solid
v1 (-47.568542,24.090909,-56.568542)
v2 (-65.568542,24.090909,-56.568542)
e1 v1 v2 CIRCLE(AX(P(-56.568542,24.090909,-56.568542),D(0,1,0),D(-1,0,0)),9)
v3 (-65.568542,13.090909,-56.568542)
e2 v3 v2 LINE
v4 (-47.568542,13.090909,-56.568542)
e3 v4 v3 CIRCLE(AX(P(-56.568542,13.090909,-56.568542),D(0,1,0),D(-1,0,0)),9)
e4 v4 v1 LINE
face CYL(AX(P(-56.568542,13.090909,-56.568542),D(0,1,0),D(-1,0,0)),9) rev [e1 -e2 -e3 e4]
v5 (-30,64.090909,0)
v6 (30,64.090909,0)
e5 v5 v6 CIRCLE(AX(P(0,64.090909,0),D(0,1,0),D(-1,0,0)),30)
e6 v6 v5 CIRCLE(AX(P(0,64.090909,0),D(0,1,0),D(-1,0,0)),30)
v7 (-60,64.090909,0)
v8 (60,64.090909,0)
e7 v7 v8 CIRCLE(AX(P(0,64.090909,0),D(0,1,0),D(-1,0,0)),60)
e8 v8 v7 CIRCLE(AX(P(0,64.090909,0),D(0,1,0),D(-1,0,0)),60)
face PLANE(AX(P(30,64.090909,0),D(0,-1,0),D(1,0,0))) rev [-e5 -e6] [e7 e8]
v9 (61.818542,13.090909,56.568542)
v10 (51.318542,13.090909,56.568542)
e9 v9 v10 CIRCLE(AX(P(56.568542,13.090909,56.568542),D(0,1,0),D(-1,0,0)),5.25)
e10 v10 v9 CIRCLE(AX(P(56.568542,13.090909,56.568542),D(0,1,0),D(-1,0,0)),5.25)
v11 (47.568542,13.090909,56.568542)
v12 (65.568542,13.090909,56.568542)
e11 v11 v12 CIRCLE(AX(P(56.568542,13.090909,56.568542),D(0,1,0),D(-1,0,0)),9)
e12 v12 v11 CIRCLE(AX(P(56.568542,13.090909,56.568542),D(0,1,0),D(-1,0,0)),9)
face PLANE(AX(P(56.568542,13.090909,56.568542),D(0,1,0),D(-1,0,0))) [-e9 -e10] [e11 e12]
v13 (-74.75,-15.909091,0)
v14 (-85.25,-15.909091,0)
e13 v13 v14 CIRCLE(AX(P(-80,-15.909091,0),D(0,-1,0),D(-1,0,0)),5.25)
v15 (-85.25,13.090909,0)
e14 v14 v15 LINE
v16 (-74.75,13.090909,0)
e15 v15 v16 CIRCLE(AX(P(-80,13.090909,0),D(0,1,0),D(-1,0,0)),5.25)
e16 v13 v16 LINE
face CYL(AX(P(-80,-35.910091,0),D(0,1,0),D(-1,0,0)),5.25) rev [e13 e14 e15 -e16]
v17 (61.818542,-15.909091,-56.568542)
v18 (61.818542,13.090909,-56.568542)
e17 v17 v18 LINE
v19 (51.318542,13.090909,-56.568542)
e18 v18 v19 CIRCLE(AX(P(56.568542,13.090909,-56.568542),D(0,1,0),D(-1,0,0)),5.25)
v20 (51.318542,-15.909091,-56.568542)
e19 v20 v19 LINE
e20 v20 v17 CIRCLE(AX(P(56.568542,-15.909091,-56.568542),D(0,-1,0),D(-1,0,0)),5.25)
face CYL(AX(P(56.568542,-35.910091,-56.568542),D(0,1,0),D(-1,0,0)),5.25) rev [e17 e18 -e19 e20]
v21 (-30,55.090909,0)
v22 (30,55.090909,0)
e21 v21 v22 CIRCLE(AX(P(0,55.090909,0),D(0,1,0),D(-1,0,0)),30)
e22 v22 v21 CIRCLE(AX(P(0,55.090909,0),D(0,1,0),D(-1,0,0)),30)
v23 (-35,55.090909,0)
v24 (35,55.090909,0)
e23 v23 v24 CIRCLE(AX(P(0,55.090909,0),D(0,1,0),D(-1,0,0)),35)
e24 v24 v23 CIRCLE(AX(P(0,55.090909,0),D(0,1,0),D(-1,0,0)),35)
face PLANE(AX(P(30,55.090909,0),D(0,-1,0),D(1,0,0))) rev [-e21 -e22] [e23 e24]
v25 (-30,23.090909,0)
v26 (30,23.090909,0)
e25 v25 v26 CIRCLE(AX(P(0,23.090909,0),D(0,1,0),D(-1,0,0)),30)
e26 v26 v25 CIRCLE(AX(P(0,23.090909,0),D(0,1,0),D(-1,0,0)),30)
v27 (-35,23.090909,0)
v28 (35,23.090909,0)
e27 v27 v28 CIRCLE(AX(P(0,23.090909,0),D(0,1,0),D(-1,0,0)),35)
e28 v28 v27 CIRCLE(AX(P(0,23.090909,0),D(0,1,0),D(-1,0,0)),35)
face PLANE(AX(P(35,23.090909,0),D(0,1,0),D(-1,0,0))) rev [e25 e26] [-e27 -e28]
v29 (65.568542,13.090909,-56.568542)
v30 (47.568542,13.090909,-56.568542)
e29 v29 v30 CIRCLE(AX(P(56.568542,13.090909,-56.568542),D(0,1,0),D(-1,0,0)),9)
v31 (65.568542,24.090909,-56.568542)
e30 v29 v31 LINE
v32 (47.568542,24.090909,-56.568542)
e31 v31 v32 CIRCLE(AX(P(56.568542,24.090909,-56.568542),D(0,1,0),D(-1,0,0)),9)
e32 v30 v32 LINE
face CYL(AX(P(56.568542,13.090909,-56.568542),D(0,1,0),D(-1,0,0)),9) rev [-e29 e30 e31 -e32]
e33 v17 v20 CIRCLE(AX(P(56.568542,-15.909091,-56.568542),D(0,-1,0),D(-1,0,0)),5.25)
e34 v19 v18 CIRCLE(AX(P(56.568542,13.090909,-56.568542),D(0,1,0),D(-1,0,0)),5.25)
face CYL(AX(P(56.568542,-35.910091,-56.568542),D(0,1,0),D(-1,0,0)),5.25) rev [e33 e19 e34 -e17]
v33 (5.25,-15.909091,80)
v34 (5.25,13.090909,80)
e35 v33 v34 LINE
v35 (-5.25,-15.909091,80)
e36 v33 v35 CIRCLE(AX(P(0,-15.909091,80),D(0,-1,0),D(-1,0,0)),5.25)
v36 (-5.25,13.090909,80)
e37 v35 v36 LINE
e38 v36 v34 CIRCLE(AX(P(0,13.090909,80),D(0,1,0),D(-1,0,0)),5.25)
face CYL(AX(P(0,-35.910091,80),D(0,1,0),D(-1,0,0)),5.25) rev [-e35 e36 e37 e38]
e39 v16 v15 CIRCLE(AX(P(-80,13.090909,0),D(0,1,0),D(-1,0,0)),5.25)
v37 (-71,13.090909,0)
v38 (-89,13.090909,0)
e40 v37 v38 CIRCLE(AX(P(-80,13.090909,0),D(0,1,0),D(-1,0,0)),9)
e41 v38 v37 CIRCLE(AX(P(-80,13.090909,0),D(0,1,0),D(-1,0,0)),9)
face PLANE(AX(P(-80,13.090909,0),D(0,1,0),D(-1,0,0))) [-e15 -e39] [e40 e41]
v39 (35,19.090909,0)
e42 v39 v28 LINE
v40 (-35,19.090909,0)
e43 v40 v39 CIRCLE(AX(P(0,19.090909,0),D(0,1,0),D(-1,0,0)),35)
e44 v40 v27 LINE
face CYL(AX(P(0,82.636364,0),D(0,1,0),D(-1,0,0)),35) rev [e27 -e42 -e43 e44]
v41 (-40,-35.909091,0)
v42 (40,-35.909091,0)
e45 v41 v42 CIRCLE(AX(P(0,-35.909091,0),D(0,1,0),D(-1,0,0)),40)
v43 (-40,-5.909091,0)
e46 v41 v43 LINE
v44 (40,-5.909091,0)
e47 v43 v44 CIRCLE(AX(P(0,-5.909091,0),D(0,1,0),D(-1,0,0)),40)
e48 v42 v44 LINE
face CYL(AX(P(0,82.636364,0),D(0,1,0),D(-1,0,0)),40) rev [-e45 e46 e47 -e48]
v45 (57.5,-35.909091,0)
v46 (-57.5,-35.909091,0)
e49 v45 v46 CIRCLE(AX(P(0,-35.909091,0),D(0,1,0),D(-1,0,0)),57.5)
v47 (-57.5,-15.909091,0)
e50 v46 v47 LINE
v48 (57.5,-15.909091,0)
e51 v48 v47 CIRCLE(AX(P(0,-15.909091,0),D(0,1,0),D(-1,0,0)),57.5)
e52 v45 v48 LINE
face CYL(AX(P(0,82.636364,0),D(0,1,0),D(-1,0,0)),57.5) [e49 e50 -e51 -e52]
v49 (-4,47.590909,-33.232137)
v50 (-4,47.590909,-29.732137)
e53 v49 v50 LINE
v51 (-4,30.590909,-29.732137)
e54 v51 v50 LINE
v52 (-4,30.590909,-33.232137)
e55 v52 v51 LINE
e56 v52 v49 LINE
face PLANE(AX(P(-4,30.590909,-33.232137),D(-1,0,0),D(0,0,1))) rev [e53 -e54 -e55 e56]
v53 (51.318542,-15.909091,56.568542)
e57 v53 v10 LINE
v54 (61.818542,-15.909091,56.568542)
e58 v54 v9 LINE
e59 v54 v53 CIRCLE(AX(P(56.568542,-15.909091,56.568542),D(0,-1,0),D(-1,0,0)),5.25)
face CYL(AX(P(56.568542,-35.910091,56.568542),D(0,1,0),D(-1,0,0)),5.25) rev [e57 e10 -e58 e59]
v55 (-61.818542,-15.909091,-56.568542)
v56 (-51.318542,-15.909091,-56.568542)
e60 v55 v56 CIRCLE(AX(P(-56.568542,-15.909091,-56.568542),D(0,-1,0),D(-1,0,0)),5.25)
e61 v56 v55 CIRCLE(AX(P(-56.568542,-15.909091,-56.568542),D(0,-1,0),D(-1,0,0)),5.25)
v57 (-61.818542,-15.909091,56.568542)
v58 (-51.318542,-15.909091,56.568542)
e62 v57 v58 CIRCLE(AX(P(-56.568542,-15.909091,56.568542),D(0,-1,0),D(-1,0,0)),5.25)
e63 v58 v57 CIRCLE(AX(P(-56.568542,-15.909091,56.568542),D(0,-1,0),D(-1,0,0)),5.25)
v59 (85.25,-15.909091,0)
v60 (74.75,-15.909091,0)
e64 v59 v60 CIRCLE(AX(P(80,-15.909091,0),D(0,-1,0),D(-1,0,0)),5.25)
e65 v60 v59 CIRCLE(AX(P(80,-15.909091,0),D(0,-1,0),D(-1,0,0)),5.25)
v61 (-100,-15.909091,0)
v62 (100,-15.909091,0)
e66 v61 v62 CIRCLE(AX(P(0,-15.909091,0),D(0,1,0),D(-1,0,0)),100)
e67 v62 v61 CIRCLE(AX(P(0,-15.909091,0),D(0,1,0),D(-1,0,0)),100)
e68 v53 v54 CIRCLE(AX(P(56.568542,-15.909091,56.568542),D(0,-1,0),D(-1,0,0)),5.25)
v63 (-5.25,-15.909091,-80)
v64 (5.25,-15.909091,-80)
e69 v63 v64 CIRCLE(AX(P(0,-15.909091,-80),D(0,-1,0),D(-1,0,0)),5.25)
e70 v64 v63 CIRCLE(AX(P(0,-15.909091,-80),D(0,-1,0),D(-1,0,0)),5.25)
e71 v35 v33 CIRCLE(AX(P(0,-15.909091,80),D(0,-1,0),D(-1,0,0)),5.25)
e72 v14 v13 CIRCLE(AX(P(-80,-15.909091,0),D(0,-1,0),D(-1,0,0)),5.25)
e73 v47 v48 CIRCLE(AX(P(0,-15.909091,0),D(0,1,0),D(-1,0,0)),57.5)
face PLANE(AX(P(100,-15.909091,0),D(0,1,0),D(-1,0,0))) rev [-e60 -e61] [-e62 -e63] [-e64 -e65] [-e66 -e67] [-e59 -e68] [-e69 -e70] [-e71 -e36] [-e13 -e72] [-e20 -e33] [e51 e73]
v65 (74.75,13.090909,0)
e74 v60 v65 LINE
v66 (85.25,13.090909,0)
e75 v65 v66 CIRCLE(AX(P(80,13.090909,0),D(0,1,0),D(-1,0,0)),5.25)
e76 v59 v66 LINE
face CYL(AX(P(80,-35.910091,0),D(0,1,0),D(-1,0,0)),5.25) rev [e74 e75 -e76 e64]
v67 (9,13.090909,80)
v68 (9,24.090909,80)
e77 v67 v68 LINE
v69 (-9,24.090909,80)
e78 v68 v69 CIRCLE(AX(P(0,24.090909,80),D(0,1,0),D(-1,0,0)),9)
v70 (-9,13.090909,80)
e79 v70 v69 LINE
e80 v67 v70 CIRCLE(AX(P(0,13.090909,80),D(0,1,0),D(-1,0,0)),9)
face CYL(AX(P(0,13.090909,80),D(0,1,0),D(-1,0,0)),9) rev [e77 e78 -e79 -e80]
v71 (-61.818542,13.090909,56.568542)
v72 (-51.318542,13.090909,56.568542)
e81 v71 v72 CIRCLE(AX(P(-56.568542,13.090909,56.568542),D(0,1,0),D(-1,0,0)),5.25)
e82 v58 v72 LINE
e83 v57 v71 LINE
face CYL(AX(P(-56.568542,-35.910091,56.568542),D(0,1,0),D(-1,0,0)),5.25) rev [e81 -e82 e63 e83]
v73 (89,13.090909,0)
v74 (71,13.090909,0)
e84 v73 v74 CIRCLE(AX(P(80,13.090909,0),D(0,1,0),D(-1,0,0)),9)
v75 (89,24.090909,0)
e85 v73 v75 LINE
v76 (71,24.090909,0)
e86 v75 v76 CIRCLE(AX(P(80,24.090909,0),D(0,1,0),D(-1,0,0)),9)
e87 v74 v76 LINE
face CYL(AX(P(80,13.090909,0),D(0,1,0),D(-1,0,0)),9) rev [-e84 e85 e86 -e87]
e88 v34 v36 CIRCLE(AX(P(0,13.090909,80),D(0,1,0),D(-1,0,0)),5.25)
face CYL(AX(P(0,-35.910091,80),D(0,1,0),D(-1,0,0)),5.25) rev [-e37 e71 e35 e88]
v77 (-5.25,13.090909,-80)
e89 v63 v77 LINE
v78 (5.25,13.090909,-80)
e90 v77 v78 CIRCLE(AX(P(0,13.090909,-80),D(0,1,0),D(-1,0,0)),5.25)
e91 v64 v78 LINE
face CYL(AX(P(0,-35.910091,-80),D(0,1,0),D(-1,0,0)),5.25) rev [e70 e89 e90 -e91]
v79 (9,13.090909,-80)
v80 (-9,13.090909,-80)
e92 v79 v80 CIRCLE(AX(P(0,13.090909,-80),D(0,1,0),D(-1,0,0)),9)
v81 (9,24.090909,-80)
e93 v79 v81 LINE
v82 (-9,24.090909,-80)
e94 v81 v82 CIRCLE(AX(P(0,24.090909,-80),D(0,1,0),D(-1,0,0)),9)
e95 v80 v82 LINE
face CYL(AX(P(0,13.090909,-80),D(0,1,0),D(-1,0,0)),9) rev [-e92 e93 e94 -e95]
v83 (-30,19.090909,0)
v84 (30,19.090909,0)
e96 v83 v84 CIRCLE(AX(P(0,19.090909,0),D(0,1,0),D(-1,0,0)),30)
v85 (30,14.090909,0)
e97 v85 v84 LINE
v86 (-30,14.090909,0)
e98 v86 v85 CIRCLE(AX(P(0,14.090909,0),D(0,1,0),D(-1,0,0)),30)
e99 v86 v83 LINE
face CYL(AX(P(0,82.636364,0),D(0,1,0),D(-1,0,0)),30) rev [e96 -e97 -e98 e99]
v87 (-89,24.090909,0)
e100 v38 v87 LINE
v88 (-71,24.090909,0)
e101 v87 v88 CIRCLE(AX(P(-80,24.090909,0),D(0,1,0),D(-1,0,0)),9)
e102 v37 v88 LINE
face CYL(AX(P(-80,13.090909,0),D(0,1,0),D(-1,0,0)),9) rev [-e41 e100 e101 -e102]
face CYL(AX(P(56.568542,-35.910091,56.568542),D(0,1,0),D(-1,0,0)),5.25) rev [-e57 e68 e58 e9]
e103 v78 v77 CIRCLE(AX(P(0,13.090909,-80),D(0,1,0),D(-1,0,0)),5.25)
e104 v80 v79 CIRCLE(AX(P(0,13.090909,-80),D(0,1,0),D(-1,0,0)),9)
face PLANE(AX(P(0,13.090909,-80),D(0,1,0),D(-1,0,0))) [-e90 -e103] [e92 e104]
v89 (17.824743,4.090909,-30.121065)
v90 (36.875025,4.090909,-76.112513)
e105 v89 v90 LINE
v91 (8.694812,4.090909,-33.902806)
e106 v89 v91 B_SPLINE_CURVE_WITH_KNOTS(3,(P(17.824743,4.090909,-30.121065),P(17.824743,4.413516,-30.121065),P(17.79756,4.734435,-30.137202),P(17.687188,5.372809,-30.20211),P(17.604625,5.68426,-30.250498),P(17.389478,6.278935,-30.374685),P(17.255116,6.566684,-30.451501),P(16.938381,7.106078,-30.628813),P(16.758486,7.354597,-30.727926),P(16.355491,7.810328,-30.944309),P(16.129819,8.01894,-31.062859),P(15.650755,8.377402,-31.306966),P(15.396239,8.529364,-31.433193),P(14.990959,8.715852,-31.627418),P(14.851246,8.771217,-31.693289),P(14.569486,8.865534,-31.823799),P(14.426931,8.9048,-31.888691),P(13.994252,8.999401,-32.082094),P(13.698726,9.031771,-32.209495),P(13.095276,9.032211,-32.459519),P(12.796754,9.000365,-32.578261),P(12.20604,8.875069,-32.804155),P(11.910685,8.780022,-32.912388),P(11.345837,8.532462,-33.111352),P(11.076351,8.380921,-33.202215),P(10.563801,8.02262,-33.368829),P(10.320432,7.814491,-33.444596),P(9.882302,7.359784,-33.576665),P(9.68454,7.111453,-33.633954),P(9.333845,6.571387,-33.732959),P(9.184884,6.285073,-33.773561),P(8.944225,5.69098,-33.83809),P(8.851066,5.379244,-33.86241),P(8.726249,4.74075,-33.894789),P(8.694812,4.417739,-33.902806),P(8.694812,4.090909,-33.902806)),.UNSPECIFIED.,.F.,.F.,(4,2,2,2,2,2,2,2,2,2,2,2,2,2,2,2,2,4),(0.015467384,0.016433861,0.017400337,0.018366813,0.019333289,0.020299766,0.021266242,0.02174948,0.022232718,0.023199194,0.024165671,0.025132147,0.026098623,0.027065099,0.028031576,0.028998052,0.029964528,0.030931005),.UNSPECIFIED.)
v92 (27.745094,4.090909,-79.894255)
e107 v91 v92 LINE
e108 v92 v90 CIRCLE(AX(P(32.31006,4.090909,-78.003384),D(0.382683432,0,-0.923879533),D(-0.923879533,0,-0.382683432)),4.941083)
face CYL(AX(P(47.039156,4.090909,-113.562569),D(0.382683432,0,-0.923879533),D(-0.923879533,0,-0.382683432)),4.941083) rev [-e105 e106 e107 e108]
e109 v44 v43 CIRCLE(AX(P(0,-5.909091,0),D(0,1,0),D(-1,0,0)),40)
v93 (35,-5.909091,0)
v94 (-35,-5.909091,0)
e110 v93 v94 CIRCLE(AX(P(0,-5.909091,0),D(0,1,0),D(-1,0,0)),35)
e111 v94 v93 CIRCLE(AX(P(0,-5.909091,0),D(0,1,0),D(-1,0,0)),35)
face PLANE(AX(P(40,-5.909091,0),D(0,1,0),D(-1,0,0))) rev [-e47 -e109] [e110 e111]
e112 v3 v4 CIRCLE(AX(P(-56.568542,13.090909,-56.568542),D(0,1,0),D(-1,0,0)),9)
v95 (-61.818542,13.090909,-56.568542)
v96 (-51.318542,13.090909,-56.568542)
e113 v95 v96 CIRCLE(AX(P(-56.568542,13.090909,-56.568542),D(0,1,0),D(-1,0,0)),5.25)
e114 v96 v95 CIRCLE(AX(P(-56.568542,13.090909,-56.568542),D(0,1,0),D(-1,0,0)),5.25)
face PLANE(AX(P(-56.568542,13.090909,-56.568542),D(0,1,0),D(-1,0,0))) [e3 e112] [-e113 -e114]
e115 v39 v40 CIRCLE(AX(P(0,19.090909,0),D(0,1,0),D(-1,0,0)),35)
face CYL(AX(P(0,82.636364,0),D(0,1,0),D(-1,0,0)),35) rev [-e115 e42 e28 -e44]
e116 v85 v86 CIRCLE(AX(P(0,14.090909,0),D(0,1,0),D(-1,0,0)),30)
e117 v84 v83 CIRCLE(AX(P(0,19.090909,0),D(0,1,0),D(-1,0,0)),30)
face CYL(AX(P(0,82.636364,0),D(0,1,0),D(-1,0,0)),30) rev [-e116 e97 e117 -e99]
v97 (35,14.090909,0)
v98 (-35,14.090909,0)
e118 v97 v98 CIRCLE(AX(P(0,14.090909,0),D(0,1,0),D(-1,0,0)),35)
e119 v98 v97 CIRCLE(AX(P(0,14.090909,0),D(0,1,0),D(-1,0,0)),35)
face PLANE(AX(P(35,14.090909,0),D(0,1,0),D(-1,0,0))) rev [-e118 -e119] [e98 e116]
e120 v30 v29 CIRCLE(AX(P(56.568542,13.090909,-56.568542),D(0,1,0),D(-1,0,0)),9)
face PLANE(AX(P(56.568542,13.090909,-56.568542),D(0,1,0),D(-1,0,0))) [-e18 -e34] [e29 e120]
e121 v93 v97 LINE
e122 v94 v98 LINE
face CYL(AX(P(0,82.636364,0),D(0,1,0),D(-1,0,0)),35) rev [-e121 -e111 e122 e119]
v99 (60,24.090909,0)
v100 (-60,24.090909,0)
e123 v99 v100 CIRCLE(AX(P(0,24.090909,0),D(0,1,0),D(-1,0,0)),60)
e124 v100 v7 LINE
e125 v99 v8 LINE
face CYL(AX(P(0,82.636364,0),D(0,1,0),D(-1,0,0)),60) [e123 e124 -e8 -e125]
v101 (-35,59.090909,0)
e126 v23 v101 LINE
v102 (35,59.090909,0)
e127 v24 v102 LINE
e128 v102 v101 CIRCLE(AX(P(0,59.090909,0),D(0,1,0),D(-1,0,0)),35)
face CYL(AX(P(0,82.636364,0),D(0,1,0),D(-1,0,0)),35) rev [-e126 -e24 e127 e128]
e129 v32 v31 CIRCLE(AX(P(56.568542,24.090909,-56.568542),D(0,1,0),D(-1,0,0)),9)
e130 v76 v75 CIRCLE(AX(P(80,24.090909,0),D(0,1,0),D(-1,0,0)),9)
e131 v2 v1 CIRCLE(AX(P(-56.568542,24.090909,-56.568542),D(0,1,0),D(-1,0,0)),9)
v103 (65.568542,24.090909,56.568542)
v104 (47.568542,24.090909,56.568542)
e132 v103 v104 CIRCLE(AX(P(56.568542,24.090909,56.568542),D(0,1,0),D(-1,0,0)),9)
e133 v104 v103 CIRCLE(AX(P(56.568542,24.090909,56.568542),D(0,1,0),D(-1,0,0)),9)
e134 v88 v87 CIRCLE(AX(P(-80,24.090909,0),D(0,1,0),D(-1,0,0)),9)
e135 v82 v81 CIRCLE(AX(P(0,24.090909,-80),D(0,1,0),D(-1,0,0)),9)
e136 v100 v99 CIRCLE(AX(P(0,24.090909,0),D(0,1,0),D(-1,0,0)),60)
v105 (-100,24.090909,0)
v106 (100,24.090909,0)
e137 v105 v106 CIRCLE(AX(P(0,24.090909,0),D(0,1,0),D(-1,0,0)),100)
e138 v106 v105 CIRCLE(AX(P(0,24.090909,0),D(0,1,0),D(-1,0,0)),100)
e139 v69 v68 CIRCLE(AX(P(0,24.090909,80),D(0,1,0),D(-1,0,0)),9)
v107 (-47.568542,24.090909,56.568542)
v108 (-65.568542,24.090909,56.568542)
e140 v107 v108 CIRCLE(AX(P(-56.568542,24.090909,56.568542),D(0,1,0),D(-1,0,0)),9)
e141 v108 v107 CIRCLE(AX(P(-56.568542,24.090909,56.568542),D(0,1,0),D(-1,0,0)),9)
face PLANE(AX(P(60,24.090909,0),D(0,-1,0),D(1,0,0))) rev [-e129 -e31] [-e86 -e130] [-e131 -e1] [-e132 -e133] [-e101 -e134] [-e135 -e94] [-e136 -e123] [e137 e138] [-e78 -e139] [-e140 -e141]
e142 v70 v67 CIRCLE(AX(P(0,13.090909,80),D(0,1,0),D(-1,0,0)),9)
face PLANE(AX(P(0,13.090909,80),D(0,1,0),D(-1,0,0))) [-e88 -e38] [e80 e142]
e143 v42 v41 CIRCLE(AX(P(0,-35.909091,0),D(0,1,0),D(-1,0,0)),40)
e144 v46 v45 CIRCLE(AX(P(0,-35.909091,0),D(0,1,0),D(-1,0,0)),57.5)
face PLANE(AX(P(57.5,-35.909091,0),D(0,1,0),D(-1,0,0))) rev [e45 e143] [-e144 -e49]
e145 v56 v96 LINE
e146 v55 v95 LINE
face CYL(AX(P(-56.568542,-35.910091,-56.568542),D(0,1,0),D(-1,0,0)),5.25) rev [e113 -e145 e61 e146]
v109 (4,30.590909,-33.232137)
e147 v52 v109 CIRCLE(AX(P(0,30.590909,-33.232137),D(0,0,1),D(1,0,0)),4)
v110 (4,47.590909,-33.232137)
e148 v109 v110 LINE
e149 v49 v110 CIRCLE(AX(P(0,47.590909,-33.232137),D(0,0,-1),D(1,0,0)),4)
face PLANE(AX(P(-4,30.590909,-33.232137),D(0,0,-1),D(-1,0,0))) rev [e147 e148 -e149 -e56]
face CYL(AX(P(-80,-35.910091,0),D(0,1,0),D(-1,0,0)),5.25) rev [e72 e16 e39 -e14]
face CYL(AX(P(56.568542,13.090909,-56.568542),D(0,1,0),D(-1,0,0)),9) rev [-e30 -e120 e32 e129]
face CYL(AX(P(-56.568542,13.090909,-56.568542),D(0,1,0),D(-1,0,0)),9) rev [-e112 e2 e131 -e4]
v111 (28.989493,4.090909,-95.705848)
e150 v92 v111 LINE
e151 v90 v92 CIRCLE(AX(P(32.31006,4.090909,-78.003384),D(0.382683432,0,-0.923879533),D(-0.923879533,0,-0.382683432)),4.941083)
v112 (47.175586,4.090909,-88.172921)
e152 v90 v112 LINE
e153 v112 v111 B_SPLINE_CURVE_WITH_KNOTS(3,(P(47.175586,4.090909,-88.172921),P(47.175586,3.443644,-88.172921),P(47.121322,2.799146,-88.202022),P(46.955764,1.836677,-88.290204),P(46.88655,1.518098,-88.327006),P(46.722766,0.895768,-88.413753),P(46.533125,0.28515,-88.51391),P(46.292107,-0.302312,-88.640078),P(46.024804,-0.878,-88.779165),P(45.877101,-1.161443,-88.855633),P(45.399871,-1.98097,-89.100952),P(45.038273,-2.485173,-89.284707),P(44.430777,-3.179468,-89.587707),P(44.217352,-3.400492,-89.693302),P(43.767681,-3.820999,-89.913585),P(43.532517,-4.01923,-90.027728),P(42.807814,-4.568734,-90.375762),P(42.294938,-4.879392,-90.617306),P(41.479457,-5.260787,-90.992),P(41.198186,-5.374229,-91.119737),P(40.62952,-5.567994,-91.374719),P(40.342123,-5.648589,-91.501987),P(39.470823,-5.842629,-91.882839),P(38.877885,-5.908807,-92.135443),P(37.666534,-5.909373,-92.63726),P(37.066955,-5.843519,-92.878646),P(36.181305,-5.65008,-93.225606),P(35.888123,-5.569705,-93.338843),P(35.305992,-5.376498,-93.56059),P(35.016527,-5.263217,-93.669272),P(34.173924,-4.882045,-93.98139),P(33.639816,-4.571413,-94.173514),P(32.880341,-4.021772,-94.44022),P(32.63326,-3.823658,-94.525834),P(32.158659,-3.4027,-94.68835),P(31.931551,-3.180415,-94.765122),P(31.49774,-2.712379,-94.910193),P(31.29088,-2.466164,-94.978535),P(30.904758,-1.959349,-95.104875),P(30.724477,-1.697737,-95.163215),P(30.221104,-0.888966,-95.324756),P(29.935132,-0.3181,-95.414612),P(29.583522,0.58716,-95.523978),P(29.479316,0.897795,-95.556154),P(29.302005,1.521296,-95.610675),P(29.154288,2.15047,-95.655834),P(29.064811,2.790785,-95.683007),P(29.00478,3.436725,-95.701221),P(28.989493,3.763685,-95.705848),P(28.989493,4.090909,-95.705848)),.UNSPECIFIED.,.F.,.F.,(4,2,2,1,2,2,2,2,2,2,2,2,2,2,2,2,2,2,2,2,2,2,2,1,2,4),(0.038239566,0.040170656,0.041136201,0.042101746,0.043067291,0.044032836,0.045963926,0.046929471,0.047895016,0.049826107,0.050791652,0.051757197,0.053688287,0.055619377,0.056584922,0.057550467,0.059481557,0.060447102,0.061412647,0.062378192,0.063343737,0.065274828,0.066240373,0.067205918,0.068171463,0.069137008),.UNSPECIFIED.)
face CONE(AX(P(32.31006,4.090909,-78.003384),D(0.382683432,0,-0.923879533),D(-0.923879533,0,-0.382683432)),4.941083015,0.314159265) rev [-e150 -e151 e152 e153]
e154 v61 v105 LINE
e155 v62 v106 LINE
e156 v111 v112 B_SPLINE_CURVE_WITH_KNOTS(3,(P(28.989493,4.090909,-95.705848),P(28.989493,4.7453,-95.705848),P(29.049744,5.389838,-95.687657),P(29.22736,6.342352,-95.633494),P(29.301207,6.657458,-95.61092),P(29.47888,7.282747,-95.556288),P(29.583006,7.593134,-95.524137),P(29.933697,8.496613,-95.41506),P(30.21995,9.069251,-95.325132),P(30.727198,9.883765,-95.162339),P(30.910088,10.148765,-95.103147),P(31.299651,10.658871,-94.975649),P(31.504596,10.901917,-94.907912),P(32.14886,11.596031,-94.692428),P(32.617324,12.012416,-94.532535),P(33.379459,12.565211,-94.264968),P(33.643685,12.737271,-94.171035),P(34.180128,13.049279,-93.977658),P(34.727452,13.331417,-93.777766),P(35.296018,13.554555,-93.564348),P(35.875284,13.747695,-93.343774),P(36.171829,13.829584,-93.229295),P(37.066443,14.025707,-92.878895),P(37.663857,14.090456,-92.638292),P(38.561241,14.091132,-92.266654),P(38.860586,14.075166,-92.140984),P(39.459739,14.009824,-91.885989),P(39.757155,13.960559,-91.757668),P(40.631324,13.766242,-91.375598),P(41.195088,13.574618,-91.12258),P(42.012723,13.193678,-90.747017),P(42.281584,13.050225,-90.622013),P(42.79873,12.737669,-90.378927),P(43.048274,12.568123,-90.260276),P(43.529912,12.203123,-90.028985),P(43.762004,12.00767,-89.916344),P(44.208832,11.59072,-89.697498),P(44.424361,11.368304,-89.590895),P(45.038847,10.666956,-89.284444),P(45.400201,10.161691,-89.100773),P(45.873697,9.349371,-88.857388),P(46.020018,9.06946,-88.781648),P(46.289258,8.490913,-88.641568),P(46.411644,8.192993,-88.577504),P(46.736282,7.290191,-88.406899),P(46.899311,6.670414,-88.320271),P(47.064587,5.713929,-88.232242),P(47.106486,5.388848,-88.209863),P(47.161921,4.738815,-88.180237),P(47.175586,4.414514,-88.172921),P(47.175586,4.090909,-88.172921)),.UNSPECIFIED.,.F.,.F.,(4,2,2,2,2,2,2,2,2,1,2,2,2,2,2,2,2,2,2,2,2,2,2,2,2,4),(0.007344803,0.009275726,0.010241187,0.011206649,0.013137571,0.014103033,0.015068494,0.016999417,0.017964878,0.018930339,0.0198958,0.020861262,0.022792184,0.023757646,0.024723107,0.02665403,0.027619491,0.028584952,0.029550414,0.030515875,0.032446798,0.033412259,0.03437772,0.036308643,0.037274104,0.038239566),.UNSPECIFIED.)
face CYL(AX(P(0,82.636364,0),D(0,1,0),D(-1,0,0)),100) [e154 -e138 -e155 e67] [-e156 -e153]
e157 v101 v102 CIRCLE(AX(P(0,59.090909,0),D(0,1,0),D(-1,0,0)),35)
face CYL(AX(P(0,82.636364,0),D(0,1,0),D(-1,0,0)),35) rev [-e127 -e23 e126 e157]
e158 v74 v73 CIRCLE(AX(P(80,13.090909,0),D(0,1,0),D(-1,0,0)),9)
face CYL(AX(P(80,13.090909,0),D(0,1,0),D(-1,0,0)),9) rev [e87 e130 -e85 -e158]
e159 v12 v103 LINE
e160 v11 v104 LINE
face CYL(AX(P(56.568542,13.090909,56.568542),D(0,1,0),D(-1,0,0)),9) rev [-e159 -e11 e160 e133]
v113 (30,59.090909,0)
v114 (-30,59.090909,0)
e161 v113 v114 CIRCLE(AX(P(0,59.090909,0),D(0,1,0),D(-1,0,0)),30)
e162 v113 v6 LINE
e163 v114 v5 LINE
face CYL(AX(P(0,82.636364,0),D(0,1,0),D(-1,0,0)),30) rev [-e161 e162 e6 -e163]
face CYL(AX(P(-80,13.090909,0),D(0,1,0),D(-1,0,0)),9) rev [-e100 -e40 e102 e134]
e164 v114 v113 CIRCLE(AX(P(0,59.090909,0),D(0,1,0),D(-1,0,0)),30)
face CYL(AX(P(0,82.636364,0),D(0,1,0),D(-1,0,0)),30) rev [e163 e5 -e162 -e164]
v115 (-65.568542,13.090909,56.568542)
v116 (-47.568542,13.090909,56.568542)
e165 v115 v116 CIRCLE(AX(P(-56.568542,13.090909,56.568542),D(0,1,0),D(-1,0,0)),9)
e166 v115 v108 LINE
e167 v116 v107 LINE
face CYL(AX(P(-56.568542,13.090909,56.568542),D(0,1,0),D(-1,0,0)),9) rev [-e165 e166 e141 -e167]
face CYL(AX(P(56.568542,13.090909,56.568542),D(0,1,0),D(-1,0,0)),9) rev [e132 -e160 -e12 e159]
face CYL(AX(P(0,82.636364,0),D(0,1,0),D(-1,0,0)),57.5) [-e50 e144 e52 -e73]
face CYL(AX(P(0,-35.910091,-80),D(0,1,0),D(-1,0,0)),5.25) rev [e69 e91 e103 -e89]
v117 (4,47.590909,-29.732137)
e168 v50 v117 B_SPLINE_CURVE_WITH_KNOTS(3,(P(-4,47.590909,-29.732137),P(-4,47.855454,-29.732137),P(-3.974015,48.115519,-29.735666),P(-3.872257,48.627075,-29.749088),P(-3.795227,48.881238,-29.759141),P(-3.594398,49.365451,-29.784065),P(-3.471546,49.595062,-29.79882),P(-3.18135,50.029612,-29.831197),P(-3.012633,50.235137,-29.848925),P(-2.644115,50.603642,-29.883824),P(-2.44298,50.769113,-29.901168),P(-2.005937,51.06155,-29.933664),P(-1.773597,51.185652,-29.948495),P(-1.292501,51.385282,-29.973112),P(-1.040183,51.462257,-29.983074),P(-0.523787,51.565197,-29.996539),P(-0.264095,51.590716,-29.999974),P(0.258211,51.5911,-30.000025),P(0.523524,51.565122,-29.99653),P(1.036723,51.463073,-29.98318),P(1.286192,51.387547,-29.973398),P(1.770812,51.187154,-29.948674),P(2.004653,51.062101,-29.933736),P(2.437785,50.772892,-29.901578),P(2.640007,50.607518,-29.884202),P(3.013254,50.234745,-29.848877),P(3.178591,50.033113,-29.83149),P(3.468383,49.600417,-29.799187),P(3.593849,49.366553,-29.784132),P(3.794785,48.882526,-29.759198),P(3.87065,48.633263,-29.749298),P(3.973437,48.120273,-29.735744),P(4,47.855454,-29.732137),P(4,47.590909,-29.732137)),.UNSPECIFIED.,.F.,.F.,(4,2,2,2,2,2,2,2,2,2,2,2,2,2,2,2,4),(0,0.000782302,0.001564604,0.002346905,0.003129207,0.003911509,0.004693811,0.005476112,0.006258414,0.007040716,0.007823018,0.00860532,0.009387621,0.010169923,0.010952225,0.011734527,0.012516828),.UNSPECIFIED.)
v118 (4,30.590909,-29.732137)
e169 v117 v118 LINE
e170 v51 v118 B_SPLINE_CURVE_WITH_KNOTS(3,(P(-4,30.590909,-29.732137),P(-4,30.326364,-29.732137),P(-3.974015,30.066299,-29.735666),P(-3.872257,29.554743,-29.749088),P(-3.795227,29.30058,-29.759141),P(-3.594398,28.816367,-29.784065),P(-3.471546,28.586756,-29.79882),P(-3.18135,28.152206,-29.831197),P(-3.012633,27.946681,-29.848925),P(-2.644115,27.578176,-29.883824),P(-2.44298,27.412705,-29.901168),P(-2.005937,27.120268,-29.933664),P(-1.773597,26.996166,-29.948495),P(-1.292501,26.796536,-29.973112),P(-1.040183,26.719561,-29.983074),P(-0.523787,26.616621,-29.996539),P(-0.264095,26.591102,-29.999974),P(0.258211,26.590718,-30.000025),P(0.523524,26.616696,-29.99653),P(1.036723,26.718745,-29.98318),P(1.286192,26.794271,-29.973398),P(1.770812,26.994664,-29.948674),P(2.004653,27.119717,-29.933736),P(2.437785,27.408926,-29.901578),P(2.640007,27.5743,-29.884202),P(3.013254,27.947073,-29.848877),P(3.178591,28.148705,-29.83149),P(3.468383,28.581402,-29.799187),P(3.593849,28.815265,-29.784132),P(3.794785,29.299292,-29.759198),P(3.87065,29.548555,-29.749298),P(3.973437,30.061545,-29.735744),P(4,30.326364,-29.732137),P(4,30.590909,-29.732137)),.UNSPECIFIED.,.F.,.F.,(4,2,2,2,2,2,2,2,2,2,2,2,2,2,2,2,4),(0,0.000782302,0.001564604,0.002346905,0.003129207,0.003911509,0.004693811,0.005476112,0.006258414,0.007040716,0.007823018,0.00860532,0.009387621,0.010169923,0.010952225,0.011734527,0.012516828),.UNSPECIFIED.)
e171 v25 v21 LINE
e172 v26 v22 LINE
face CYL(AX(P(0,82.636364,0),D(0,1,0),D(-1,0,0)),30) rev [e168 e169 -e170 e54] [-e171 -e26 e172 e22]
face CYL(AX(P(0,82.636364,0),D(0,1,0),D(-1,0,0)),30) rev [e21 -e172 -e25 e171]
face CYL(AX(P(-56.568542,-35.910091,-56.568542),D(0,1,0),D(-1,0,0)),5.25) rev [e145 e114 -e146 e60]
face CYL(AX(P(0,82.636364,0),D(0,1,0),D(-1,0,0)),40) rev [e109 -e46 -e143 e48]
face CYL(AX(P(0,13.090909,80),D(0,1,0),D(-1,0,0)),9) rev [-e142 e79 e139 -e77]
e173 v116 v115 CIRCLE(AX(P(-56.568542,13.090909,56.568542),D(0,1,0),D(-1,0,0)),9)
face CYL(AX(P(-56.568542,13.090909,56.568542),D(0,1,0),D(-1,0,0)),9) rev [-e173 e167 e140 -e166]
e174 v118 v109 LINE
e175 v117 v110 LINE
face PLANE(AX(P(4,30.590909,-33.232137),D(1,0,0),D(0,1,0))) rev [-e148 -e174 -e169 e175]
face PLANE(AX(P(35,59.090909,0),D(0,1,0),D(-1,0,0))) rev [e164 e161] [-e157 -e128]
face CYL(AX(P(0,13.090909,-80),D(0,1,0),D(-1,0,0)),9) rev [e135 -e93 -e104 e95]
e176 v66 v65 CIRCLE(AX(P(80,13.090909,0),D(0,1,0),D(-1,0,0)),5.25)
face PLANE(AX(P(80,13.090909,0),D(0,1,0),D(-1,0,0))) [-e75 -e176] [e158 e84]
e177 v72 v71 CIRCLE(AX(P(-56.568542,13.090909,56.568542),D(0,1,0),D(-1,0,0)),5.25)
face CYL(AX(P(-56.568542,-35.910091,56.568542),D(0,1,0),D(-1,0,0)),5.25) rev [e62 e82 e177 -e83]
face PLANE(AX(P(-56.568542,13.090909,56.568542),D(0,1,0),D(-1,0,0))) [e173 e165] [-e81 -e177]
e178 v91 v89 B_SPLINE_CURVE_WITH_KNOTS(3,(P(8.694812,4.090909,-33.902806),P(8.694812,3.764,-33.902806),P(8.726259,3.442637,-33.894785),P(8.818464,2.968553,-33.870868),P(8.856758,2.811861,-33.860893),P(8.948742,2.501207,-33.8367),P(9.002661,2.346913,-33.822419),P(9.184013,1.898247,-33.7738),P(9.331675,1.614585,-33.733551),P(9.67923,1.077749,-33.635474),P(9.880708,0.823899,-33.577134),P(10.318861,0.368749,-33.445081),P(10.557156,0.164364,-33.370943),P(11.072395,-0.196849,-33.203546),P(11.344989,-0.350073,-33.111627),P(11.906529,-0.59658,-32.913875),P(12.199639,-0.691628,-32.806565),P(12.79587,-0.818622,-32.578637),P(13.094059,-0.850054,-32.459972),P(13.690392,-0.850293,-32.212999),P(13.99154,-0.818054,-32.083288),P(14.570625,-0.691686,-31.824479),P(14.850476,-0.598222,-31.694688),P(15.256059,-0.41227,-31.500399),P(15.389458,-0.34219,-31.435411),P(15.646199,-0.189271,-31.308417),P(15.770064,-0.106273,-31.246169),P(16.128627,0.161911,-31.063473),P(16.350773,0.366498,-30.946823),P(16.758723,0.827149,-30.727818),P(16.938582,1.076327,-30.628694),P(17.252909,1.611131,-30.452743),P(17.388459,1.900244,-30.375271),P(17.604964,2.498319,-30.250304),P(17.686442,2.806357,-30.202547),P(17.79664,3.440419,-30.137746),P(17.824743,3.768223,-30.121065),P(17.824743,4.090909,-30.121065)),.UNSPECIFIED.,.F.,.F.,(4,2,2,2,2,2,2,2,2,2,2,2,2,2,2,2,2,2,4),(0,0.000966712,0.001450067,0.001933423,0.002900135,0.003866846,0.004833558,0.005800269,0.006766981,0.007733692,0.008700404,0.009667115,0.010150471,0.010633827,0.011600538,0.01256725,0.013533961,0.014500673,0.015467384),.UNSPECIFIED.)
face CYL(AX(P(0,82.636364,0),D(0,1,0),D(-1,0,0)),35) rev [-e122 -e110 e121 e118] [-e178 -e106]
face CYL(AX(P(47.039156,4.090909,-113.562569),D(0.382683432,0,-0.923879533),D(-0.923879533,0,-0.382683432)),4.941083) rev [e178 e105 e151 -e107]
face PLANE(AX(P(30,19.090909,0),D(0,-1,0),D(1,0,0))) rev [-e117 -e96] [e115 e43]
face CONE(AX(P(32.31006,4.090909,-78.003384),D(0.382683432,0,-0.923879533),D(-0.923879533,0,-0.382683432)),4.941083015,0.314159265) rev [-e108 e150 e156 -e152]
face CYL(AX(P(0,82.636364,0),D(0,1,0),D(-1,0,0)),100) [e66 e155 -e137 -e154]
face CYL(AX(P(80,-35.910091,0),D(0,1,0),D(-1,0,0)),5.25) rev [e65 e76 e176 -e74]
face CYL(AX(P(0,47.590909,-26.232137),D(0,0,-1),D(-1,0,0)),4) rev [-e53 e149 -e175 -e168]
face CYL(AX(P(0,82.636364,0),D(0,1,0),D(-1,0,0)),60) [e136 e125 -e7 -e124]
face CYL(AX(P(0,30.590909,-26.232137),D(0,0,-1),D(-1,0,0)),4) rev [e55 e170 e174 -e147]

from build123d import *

# Parameters (mm, degrees)
SKETCH_2_R          = 9
CUT_EXTRUDE_1_DEPTH = 11
CUT_EXTRUDE_2_REACH = 152.336
SKETCH_3_R          = 5.25
CUT_EXTRUDE_START   = -7.5
SKETCH_6_W          = 8
SKETCH_6_H          = 7
CUT_EXTRUDE_3_DEPTH = 17
CUT_EXTRUDE_4_DEPTH = 7


with BuildPart() as part:
    # 草图1 → 旋转1 (revolve)
    with BuildSketch(Plane.XY, mode=Mode.PRIVATE) as revolve_1_sk:
        Polygon((30, 64.090909091), (60, 64.090909091), (60, 24.090909091), (100, 24.090909091), (100, -15.909090909), (57.5, -15.909090909), (57.5, -35.909090909), (40, -35.909090909), (40, -5.909090909), (35, -5.909090909), (35, 14.090909091), (30, 14.090909091), (30, 19.090909091), (35, 19.090909091), (35, 23.090909091), (30, 23.090909091), (30, 55.090909091), (35, 55.090909091), (35, 59.090909091), (30, 59.090909091), align=None)
    revolve(revolve_1_sk.sketch.rotate(Axis((0, 82.636363636, 0), (0, -1, 0)), 180), axis=Axis((0, 82.636363636, 0), (0, -1, 0)))

    # 草图2 → 切除-拉伸1 (cut)
    with BuildSketch(Plane(origin=(0, 24.090909091, 0), x_dir=(1, 0, 0), z_dir=(0, 1, 0))):
        with Locations(Location((80, 0, 0), (0, 0, 180))):
            Circle(SKETCH_2_R)
        with Locations(Location((56.568542495, -56.568542495, 0), (0, 0, 180))):
            Circle(SKETCH_2_R)
        with Locations(Location((0, -80, 0), (0, 0, 180))):
            Circle(SKETCH_2_R)
        with Locations(Location((-56.568542495, -56.568542495, 0), (0, 0, 180))):
            Circle(SKETCH_2_R)
        with Locations(Location((-80, 0, 0), (0, 0, 180))):
            Circle(SKETCH_2_R)
        with Locations(Location((-56.568542495, 56.568542495, 0), (0, 0, 180))):
            Circle(SKETCH_2_R)
        with Locations(Location((0, 80, 0), (0, 0, 180))):
            Circle(SKETCH_2_R)
        with Locations(Location((56.568542495, 56.568542495, 0), (0, 0, 180))):
            Circle(SKETCH_2_R)
    extrude(amount=-CUT_EXTRUDE_1_DEPTH, mode=Mode.SUBTRACT)

    # 草图3 → 切除-拉伸2 (cut, up to next)
    with BuildSketch(Plane(origin=(0, 13.090909091, 0), x_dir=(1, 0, 0), z_dir=(0, 1, 0)), mode=Mode.PRIVATE) as cut_extrude_2_sk1:
        with Locations(Location((56.568542495, 56.568542495, 0), (0, 0, 180))):
            Circle(SKETCH_3_R)
    cut_extrude_2_tool1 = extrude(cut_extrude_2_sk1.sketch, amount=-CUT_EXTRUDE_2_REACH, mode=Mode.PRIVATE) & part.part
    # 草图3 → 切除-拉伸2 (cut, up to next)
    with BuildSketch(Plane(origin=(0, 13.090909091, 0), x_dir=(1, 0, 0), z_dir=(0, 1, 0)), mode=Mode.PRIVATE) as cut_extrude_2_sk2:
        with Locations(Location((80, 0, 0), (0, 0, 180))):
            Circle(SKETCH_3_R)
    cut_extrude_2_tool2 = extrude(cut_extrude_2_sk2.sketch, amount=-CUT_EXTRUDE_2_REACH, mode=Mode.PRIVATE) & part.part
    # 草图3 → 切除-拉伸2 (cut, up to next)
    with BuildSketch(Plane(origin=(0, 13.090909091, 0), x_dir=(1, 0, 0), z_dir=(0, 1, 0)), mode=Mode.PRIVATE) as cut_extrude_2_sk3:
        with Locations(Location((56.568542495, -56.568542495, 0), (0, 0, 180))):
            Circle(SKETCH_3_R)
    cut_extrude_2_tool3 = extrude(cut_extrude_2_sk3.sketch, amount=-CUT_EXTRUDE_2_REACH, mode=Mode.PRIVATE) & part.part
    # 草图3 → 切除-拉伸2 (cut, up to next)
    with BuildSketch(Plane(origin=(0, 13.090909091, 0), x_dir=(1, 0, 0), z_dir=(0, 1, 0)), mode=Mode.PRIVATE) as cut_extrude_2_sk4:
        with Locations(Location((0, -80, 0), (0, 0, 180))):
            Circle(SKETCH_3_R)
    cut_extrude_2_tool4 = extrude(cut_extrude_2_sk4.sketch, amount=-CUT_EXTRUDE_2_REACH, mode=Mode.PRIVATE) & part.part
    # 草图3 → 切除-拉伸2 (cut, up to next)
    with BuildSketch(Plane(origin=(0, 13.090909091, 0), x_dir=(1, 0, 0), z_dir=(0, 1, 0)), mode=Mode.PRIVATE) as cut_extrude_2_sk5:
        with Locations(Location((-56.568542495, -56.568542495, 0), (0, 0, 180))):
            Circle(SKETCH_3_R)
    cut_extrude_2_tool5 = extrude(cut_extrude_2_sk5.sketch, amount=-CUT_EXTRUDE_2_REACH, mode=Mode.PRIVATE) & part.part
    # 草图3 → 切除-拉伸2 (cut, up to next)
    with BuildSketch(Plane(origin=(0, 13.090909091, 0), x_dir=(1, 0, 0), z_dir=(0, 1, 0)), mode=Mode.PRIVATE) as cut_extrude_2_sk6:
        with Locations(Location((-80, 0, 0), (0, 0, 180))):
            Circle(SKETCH_3_R)
    cut_extrude_2_tool6 = extrude(cut_extrude_2_sk6.sketch, amount=-CUT_EXTRUDE_2_REACH, mode=Mode.PRIVATE) & part.part
    # 草图3 → 切除-拉伸2 (cut, up to next)
    with BuildSketch(Plane(origin=(0, 13.090909091, 0), x_dir=(1, 0, 0), z_dir=(0, 1, 0)), mode=Mode.PRIVATE) as cut_extrude_2_sk7:
        with Locations(Location((-56.568542495, 56.568542495, 0), (0, 0, 180))):
            Circle(SKETCH_3_R)
    cut_extrude_2_tool7 = extrude(cut_extrude_2_sk7.sketch, amount=-CUT_EXTRUDE_2_REACH, mode=Mode.PRIVATE) & part.part
    # 草图3 → 切除-拉伸2 (cut, up to next)
    with BuildSketch(Plane(origin=(0, 13.090909091, 0), x_dir=(1, 0, 0), z_dir=(0, 1, 0)), mode=Mode.PRIVATE) as cut_extrude_2_sk8:
        with Locations(Location((0, 80, 0), (0, 0, 180))):
            Circle(SKETCH_3_R)
    cut_extrude_2_tool8 = extrude(cut_extrude_2_sk8.sketch, amount=-CUT_EXTRUDE_2_REACH, mode=Mode.PRIVATE) & part.part
    add(cut_extrude_2_tool1.solids().sort_by_distance((56.568542, 13.090909, -56.568542))[0], mode=Mode.SUBTRACT)
    add(cut_extrude_2_tool2.solids().sort_by_distance((80, 13.090909, 0))[0], mode=Mode.SUBTRACT)
    add(cut_extrude_2_tool3.solids().sort_by_distance((56.568542, 13.090909, 56.568542))[0], mode=Mode.SUBTRACT)
    add(cut_extrude_2_tool4.solids().sort_by_distance((0, 13.090909, 80))[0], mode=Mode.SUBTRACT)
    add(cut_extrude_2_tool5.solids().sort_by_distance((-56.568542, 13.090909, 56.568542))[0], mode=Mode.SUBTRACT)
    add(cut_extrude_2_tool6.solids().sort_by_distance((-80, 13.090909, 0))[0], mode=Mode.SUBTRACT)
    add(cut_extrude_2_tool7.solids().sort_by_distance((-56.568542, 13.090909, -56.568542))[0], mode=Mode.SUBTRACT)
    add(cut_extrude_2_tool8.solids().sort_by_distance((0, 13.090909, -80))[0], mode=Mode.SUBTRACT)

    # 草图5 → 切除-旋转1 (revolve, cut)
    with BuildSketch(Plane(origin=(0, 0, 0), x_dir=(0, -1, 0), z_dir=(0.9238795325112864, 0, 0.38268343236509056)), mode=Mode.PRIVATE) as cut_revolve_1_sk:
        Polygon((-4.090909091, 100), (5.909090909, 100), (0.850173924, 84.430254481), (0.850173924, 3.622054485), (-4.090909091, 3.622054485), align=None)
    revolve(cut_revolve_1_sk.sketch.rotate(Axis((47.039156362, 4.090909091, -113.562569252), (-0.3826834323650906, 0, 0.9238795325112864)), 270), axis=Axis((47.039156362, 4.090909091, -113.562569252), (-0.3826834323650906, 0, 0.9238795325112864)), mode=Mode.SUBTRACT)

    # 草图6 → 切除-拉伸3 (cut)
    with BuildSketch(Plane(origin=(0, 55.090909091, 0), x_dir=(1, 0, 0), z_dir=(0, 1, 0)).offset(CUT_EXTRUDE_START)):
        with Locations((0, 29.732137495)):
            Rectangle(SKETCH_6_W, SKETCH_6_H)
    extrude(amount=-CUT_EXTRUDE_3_DEPTH, mode=Mode.SUBTRACT)

    # 草图7 → 切除-拉伸4 (cut)
    with BuildSketch(Plane.XY.offset(-33.232137495)):
        with BuildLine():
            ThreePointArc((-4, 47.590909091), (0, 51.590909091), (4, 47.590909091))
            Line((4, 47.590909091), (-4, 47.590909091))
        make_face()
        with BuildLine():
            ThreePointArc((-4, 30.590909091), (0, 26.590909091), (4, 30.590909091))
            Line((4, 30.590909091), (-4, 30.590909091))
        make_face()
    extrude(amount=CUT_EXTRUDE_4_DEPTH, mode=Mode.SUBTRACT)


solid = part.part
